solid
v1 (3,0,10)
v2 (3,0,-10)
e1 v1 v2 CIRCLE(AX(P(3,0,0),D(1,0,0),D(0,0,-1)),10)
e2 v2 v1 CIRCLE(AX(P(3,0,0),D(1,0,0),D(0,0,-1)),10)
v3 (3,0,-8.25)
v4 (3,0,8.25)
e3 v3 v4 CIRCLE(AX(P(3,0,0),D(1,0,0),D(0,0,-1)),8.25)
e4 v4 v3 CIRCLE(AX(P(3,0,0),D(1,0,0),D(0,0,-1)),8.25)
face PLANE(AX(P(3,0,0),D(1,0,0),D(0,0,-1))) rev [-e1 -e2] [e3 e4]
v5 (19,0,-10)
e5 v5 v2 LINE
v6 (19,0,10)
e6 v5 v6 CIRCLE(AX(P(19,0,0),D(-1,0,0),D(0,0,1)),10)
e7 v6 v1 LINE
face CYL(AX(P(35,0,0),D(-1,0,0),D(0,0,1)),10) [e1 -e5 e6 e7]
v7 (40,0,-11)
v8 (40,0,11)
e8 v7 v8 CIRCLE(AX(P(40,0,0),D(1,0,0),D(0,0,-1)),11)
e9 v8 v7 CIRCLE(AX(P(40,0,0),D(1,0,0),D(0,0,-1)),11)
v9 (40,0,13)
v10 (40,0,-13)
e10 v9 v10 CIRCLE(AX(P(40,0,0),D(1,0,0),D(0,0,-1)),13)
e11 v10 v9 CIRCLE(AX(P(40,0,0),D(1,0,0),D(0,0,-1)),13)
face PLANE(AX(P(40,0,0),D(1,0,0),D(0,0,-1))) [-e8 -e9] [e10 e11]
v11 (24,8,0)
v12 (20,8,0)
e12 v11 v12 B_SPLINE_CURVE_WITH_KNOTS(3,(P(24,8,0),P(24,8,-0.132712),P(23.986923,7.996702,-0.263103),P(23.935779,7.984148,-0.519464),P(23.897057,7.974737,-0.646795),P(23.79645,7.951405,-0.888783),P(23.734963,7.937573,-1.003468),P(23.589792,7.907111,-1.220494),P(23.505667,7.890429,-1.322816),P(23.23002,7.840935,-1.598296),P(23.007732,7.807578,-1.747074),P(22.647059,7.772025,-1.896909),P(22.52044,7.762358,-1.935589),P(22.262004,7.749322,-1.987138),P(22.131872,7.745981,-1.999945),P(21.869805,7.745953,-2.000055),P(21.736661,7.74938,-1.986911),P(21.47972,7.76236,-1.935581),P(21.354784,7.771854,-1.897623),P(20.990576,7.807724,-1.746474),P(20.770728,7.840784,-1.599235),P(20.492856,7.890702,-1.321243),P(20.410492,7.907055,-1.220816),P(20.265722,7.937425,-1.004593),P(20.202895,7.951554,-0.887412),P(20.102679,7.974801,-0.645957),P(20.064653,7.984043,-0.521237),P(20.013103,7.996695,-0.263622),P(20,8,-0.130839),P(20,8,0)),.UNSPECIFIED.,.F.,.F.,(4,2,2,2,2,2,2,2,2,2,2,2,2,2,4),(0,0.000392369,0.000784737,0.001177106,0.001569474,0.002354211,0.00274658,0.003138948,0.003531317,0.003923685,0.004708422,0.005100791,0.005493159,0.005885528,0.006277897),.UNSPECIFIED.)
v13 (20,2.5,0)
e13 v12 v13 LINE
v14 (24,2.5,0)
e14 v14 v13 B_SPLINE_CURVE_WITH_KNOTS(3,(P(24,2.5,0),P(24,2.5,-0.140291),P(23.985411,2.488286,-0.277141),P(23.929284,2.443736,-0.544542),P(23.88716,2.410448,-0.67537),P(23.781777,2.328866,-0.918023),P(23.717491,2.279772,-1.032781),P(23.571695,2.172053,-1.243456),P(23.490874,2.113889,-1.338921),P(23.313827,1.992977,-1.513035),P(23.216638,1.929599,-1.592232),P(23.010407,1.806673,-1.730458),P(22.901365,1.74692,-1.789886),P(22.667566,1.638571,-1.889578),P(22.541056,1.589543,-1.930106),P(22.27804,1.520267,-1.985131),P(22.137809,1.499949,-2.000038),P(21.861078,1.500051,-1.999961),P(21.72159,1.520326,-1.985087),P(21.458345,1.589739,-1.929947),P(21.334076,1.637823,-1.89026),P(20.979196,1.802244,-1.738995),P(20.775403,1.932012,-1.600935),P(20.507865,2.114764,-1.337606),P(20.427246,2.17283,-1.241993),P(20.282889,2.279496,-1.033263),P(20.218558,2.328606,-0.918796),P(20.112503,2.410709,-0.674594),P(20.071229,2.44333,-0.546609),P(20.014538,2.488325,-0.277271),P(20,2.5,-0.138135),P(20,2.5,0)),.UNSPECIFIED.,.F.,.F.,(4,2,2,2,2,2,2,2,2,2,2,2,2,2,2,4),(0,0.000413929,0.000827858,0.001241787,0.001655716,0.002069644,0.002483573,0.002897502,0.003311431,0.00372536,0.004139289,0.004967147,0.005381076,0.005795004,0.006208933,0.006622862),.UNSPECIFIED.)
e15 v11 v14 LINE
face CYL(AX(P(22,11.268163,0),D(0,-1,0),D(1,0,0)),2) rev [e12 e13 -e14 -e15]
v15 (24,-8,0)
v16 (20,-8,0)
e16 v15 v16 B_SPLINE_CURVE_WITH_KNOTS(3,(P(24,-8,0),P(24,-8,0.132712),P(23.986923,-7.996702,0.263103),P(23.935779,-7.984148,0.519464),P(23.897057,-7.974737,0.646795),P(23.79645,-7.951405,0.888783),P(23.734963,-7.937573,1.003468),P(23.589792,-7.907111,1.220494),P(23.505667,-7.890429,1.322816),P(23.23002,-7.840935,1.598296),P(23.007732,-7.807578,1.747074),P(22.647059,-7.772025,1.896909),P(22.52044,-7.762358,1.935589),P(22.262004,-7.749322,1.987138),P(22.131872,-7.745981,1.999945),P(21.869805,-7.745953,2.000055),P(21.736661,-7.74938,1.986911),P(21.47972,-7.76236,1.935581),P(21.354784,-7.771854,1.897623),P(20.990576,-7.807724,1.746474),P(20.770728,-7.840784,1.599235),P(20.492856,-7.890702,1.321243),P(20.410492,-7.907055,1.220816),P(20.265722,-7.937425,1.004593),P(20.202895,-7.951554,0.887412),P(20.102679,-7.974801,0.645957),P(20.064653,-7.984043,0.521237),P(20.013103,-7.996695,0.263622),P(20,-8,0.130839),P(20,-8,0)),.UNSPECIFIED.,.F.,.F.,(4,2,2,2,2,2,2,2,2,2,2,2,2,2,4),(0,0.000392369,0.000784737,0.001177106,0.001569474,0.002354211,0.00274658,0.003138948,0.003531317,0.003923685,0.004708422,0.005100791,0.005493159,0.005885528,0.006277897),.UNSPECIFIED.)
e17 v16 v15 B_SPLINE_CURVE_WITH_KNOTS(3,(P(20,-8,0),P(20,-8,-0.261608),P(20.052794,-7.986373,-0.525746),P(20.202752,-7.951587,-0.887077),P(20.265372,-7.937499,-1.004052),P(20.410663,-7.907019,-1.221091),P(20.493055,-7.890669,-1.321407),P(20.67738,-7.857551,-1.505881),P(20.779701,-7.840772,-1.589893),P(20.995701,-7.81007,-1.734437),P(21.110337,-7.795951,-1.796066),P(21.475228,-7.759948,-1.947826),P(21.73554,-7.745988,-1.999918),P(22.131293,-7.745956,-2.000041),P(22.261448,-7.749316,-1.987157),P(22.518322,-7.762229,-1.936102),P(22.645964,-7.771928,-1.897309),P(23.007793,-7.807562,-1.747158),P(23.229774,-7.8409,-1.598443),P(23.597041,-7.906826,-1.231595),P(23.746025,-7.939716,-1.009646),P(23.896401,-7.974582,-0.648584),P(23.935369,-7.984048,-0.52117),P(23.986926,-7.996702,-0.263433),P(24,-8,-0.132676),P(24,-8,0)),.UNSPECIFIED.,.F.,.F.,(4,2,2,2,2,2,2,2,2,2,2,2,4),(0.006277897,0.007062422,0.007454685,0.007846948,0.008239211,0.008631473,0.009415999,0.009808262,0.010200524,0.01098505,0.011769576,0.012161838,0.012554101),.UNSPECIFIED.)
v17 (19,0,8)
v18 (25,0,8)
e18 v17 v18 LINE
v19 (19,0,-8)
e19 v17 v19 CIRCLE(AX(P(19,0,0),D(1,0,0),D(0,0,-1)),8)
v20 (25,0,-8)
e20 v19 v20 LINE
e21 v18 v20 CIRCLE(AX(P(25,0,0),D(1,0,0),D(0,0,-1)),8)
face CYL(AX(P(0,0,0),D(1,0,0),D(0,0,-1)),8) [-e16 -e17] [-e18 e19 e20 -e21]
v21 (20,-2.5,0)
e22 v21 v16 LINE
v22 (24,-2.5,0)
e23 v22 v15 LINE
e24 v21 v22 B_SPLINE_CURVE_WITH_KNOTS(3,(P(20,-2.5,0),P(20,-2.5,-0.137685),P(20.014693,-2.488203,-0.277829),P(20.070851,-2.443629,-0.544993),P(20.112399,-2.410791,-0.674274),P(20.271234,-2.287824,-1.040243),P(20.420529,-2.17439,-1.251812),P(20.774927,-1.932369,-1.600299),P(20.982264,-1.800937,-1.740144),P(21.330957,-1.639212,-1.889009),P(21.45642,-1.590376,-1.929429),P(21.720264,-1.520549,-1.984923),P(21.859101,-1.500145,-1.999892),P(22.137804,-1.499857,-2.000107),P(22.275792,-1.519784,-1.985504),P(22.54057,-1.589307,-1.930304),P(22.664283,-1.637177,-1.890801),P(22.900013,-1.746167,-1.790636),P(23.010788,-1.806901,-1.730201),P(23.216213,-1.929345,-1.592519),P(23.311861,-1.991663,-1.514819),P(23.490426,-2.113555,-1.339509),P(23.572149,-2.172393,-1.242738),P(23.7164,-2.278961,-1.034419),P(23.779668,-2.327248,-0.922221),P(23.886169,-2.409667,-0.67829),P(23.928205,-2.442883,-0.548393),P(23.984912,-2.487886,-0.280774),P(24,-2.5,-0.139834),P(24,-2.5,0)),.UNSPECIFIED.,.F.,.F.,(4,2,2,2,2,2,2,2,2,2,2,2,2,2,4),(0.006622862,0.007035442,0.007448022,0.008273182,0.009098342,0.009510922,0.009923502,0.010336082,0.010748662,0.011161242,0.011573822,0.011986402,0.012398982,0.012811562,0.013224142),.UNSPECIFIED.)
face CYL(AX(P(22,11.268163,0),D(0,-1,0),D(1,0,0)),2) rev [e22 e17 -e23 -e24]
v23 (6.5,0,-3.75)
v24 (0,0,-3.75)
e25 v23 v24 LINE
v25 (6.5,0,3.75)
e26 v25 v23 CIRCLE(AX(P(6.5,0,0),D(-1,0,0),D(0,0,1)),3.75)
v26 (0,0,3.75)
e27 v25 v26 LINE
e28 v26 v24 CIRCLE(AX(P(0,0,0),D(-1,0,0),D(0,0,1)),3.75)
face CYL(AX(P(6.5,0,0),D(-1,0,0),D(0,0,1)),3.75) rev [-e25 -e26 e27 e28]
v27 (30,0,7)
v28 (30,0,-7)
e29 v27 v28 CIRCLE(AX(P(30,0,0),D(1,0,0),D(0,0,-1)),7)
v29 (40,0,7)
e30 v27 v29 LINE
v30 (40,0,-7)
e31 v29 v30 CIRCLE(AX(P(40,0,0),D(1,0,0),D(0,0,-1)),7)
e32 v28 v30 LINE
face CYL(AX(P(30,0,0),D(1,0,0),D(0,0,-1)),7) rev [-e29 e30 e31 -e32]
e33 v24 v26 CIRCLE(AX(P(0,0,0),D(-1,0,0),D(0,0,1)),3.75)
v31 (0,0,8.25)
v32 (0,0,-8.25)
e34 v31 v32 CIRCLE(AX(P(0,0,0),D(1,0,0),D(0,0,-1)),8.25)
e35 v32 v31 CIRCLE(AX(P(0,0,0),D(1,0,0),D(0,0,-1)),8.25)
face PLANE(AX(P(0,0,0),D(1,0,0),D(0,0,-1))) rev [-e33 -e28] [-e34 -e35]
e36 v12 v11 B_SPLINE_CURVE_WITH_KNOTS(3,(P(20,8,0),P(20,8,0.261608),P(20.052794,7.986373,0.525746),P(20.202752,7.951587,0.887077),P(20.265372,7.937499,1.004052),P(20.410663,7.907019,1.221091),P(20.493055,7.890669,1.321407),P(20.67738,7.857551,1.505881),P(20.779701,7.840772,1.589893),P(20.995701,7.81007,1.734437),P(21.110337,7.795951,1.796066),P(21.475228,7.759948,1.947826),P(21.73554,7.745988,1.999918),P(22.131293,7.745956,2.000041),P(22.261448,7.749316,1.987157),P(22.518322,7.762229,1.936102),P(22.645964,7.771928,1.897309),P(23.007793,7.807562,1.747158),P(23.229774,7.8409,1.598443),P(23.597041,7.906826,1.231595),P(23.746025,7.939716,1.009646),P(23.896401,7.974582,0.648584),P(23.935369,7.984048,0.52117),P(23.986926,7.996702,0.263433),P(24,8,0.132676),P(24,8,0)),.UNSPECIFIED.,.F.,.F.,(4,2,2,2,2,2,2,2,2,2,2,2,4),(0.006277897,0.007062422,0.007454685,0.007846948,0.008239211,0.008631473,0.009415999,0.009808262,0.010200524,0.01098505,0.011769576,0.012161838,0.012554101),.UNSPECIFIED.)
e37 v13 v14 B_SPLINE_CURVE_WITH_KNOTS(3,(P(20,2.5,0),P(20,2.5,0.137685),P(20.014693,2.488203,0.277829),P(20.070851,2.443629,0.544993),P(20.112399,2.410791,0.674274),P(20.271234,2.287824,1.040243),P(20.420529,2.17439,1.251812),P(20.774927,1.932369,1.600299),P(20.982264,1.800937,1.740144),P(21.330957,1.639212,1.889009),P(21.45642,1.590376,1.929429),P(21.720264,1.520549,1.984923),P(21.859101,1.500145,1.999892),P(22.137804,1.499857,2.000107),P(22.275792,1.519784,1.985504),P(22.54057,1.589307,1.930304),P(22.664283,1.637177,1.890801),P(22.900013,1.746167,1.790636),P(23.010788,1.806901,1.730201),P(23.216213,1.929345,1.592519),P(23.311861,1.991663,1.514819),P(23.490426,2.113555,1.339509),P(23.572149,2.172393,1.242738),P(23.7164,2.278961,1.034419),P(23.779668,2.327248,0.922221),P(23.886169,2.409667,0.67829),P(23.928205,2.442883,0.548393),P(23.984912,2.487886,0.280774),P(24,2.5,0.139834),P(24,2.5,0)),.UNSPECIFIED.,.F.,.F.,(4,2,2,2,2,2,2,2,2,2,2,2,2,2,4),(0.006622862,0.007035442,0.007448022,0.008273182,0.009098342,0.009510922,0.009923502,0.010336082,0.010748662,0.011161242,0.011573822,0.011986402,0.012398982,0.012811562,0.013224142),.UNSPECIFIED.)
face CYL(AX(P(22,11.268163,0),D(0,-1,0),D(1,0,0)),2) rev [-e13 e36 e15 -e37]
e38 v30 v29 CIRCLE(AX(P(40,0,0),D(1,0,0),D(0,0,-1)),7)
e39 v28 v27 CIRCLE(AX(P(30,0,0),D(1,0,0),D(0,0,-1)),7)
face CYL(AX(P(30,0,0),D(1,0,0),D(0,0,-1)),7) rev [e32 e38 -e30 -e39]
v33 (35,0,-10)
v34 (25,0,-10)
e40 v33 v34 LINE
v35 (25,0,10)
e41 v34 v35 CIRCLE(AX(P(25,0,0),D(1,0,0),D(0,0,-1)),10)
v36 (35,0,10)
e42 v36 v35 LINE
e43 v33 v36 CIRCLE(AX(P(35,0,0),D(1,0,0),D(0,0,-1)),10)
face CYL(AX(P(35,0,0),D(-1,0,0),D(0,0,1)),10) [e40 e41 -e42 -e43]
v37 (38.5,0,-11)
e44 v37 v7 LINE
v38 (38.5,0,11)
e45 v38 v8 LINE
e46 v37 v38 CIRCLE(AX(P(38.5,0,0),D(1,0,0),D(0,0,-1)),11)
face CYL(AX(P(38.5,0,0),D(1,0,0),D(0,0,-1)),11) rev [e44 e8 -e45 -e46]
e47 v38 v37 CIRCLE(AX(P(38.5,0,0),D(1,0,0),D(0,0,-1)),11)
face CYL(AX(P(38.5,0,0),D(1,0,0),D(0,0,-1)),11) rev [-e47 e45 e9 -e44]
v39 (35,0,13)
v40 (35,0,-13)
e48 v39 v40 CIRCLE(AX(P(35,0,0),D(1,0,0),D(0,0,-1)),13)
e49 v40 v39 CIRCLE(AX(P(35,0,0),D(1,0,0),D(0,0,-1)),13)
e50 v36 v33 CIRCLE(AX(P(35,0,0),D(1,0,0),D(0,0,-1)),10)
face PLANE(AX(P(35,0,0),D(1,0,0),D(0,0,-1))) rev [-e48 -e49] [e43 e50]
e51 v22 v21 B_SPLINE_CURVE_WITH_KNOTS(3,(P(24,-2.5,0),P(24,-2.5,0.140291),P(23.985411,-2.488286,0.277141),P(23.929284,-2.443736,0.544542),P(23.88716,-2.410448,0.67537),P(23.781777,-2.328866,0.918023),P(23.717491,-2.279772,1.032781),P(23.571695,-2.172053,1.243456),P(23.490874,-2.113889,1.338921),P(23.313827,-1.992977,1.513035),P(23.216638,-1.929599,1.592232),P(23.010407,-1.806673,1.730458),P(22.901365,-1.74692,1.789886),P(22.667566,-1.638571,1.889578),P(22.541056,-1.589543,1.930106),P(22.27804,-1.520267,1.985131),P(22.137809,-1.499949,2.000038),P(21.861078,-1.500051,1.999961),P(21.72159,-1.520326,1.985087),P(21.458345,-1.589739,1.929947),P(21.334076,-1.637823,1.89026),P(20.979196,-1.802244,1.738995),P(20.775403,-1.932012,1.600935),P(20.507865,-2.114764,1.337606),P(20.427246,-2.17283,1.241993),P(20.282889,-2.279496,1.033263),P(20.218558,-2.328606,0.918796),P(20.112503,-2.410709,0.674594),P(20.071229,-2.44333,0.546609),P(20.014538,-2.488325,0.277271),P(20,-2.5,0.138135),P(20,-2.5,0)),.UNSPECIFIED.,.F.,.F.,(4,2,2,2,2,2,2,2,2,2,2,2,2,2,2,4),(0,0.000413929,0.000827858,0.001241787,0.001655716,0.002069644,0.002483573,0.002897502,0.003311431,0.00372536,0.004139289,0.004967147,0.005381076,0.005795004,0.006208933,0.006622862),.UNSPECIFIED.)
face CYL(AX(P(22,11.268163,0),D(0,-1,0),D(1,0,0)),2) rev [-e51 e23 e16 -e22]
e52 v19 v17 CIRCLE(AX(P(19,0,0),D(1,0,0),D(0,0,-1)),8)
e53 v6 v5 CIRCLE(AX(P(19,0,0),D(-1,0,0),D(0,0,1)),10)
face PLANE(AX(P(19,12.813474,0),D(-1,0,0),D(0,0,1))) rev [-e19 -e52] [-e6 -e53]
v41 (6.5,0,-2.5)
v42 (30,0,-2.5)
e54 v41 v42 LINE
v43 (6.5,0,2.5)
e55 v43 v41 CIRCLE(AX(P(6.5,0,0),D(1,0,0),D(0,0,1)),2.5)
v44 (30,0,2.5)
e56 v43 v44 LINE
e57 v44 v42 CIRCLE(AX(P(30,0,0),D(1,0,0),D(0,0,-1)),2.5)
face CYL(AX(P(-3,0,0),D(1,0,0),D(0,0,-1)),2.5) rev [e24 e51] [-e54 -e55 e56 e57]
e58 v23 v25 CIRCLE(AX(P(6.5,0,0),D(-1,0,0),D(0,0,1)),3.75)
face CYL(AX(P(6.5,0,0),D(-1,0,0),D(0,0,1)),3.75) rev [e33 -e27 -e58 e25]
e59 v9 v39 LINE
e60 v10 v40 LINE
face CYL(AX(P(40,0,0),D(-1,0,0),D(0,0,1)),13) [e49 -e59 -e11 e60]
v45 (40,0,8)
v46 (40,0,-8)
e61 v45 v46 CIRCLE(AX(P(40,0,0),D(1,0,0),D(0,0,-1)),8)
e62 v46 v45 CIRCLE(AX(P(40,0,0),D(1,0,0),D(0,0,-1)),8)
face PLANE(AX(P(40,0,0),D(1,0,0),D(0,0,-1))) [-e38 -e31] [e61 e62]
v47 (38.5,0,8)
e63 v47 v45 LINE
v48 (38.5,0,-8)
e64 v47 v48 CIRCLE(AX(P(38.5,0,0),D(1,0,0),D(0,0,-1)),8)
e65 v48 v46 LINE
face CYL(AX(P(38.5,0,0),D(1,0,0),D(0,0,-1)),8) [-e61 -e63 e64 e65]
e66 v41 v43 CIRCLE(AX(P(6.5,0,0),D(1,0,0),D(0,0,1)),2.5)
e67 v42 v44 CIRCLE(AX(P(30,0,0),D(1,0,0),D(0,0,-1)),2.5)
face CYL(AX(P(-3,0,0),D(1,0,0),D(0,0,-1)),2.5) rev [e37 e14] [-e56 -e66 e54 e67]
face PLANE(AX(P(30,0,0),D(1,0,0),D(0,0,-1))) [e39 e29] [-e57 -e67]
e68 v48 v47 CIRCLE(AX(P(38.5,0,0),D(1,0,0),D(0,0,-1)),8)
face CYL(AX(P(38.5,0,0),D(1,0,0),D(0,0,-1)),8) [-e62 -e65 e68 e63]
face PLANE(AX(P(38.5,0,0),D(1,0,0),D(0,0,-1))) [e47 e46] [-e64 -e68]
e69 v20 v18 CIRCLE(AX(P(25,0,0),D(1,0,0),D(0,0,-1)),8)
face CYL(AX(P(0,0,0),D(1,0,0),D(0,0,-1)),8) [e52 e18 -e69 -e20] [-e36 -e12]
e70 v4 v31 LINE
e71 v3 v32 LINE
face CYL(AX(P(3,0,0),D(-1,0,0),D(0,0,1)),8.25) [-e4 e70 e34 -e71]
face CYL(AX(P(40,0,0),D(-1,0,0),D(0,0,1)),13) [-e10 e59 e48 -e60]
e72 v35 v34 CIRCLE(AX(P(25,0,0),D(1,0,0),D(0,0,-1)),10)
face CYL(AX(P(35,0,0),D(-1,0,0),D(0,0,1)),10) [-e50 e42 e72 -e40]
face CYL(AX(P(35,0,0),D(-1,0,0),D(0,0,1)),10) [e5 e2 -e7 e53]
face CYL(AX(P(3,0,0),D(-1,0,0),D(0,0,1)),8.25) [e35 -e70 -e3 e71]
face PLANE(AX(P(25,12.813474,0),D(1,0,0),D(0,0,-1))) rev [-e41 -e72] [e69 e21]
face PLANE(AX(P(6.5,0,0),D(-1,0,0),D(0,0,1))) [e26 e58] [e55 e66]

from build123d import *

# Parameters (mm, degrees)
SKETCH1_R            = 8.25
BOSS_EXTRUDE1_DEPTH  = 3
SKETCH2_R            = 10
BOSS_EXTRUDE2_DEPTH  = 32
SKETCH4_R            = 13
BOSS_EXTRUDE3_DEPTH  = 5
SKETCH5_R            = 7
CUT_EXTRUDE1_DEPTH   = 10
SKETCH6_R            = 2.5
CUT_EXTRUDE2_DEPTH   = 33
SKETCH7_R            = 3.75
CUT_EXTRUDE3_DEPTH   = 6.5
CUT_SWEEP1_PROFILE_R = 2
SKETCH15_W           = 6
SKETCH15_H           = 4.8134745
CUT_EXTRUDE4_START   = -1.5
SKETCH17_R           = 11
SKETCH17_R_2         = 8
CUT_EXTRUDE4_DEPTH   = 1.5


with BuildPart() as part:
    # Sketch1 → Boss-Extrude1 (new body)
    with BuildSketch(Plane(origin=(0, 0, 0), x_dir=(0, 0, -1), z_dir=(1, 0, 0))):
        Circle(SKETCH1_R)
    extrude(amount=BOSS_EXTRUDE1_DEPTH)

    # Sketch2 → Boss-Extrude2 (add)
    with BuildSketch(Plane(origin=(3, 0, 0), x_dir=(0, 0, -1), z_dir=(1, 0, 0))):
        Circle(SKETCH2_R)
    extrude(amount=BOSS_EXTRUDE2_DEPTH)

    # Sketch4 → Boss-Extrude3 (add)
    with BuildSketch(Plane(origin=(35, 0, 0), x_dir=(0, 0, -1), z_dir=(1, 0, 0))):
        Circle(SKETCH4_R)
    extrude(amount=BOSS_EXTRUDE3_DEPTH)

    # Sketch5 → Cut-Extrude1 (cut)
    with BuildSketch(Plane(origin=(40, 0, 0), x_dir=(0, 0, -1), z_dir=(1, 0, 0))):
        Circle(SKETCH5_R)
    extrude(amount=-CUT_EXTRUDE1_DEPTH, mode=Mode.SUBTRACT)

    # Sketch6 → Cut-Extrude2 (cut)
    with BuildSketch(Plane(origin=(30, 0, 0), x_dir=(0, 0, -1), z_dir=(1, 0, 0))):
        Circle(SKETCH6_R)
    extrude(amount=-CUT_EXTRUDE2_DEPTH, mode=Mode.SUBTRACT)

    # Sketch7 → Cut-Extrude3 (cut)
    with BuildSketch(Plane.ZY):
        Circle(SKETCH7_R)
    extrude(amount=-CUT_EXTRUDE3_DEPTH, mode=Mode.SUBTRACT)

    # Cut-Sweep1: sweep along a path in Sketch8
    with BuildLine(Plane.XY) as cut_sweep1_path:
        Line((22, 11.268162534), (22, -10.569361757))
    # Cut-Sweep1 profile (on start of the path) → Cut-Sweep1 (sweep, cut)
    with BuildSketch(Plane(origin=(22, 11.268162534, 0), x_dir=(-1, 0, 0), z_dir=(0, -1, 0))):
        Circle(CUT_SWEEP1_PROFILE_R)
    sweep(path=cut_sweep1_path.line, mode=Mode.SUBTRACT)

    # Sketch15 → Cut-Revolve1 (revolve, cut)
    with BuildSketch(Plane.XY, mode=Mode.PRIVATE) as cut_revolve1_sk:
        with Locations((22, 10.40673725)):
            Rectangle(SKETCH15_W, SKETCH15_H)
    revolve(cut_revolve1_sk.sketch.rotate(Axis((0, 0, 0), (-1, 0, 0)), 90), axis=Axis((0, 0, 0), (-1, 0, 0)), mode=Mode.SUBTRACT)

    # Sketch17 → Cut-Extrude4 (cut)
    with BuildSketch(Plane(origin=(40, 0, 0), x_dir=(0, 0, -1), z_dir=(1, 0, 0)).offset(CUT_EXTRUDE4_START)):
        Circle(SKETCH17_R)
        Circle(SKETCH17_R_2, mode=Mode.SUBTRACT)
    extrude(amount=CUT_EXTRUDE4_DEPTH, mode=Mode.SUBTRACT)


solid = part.part
